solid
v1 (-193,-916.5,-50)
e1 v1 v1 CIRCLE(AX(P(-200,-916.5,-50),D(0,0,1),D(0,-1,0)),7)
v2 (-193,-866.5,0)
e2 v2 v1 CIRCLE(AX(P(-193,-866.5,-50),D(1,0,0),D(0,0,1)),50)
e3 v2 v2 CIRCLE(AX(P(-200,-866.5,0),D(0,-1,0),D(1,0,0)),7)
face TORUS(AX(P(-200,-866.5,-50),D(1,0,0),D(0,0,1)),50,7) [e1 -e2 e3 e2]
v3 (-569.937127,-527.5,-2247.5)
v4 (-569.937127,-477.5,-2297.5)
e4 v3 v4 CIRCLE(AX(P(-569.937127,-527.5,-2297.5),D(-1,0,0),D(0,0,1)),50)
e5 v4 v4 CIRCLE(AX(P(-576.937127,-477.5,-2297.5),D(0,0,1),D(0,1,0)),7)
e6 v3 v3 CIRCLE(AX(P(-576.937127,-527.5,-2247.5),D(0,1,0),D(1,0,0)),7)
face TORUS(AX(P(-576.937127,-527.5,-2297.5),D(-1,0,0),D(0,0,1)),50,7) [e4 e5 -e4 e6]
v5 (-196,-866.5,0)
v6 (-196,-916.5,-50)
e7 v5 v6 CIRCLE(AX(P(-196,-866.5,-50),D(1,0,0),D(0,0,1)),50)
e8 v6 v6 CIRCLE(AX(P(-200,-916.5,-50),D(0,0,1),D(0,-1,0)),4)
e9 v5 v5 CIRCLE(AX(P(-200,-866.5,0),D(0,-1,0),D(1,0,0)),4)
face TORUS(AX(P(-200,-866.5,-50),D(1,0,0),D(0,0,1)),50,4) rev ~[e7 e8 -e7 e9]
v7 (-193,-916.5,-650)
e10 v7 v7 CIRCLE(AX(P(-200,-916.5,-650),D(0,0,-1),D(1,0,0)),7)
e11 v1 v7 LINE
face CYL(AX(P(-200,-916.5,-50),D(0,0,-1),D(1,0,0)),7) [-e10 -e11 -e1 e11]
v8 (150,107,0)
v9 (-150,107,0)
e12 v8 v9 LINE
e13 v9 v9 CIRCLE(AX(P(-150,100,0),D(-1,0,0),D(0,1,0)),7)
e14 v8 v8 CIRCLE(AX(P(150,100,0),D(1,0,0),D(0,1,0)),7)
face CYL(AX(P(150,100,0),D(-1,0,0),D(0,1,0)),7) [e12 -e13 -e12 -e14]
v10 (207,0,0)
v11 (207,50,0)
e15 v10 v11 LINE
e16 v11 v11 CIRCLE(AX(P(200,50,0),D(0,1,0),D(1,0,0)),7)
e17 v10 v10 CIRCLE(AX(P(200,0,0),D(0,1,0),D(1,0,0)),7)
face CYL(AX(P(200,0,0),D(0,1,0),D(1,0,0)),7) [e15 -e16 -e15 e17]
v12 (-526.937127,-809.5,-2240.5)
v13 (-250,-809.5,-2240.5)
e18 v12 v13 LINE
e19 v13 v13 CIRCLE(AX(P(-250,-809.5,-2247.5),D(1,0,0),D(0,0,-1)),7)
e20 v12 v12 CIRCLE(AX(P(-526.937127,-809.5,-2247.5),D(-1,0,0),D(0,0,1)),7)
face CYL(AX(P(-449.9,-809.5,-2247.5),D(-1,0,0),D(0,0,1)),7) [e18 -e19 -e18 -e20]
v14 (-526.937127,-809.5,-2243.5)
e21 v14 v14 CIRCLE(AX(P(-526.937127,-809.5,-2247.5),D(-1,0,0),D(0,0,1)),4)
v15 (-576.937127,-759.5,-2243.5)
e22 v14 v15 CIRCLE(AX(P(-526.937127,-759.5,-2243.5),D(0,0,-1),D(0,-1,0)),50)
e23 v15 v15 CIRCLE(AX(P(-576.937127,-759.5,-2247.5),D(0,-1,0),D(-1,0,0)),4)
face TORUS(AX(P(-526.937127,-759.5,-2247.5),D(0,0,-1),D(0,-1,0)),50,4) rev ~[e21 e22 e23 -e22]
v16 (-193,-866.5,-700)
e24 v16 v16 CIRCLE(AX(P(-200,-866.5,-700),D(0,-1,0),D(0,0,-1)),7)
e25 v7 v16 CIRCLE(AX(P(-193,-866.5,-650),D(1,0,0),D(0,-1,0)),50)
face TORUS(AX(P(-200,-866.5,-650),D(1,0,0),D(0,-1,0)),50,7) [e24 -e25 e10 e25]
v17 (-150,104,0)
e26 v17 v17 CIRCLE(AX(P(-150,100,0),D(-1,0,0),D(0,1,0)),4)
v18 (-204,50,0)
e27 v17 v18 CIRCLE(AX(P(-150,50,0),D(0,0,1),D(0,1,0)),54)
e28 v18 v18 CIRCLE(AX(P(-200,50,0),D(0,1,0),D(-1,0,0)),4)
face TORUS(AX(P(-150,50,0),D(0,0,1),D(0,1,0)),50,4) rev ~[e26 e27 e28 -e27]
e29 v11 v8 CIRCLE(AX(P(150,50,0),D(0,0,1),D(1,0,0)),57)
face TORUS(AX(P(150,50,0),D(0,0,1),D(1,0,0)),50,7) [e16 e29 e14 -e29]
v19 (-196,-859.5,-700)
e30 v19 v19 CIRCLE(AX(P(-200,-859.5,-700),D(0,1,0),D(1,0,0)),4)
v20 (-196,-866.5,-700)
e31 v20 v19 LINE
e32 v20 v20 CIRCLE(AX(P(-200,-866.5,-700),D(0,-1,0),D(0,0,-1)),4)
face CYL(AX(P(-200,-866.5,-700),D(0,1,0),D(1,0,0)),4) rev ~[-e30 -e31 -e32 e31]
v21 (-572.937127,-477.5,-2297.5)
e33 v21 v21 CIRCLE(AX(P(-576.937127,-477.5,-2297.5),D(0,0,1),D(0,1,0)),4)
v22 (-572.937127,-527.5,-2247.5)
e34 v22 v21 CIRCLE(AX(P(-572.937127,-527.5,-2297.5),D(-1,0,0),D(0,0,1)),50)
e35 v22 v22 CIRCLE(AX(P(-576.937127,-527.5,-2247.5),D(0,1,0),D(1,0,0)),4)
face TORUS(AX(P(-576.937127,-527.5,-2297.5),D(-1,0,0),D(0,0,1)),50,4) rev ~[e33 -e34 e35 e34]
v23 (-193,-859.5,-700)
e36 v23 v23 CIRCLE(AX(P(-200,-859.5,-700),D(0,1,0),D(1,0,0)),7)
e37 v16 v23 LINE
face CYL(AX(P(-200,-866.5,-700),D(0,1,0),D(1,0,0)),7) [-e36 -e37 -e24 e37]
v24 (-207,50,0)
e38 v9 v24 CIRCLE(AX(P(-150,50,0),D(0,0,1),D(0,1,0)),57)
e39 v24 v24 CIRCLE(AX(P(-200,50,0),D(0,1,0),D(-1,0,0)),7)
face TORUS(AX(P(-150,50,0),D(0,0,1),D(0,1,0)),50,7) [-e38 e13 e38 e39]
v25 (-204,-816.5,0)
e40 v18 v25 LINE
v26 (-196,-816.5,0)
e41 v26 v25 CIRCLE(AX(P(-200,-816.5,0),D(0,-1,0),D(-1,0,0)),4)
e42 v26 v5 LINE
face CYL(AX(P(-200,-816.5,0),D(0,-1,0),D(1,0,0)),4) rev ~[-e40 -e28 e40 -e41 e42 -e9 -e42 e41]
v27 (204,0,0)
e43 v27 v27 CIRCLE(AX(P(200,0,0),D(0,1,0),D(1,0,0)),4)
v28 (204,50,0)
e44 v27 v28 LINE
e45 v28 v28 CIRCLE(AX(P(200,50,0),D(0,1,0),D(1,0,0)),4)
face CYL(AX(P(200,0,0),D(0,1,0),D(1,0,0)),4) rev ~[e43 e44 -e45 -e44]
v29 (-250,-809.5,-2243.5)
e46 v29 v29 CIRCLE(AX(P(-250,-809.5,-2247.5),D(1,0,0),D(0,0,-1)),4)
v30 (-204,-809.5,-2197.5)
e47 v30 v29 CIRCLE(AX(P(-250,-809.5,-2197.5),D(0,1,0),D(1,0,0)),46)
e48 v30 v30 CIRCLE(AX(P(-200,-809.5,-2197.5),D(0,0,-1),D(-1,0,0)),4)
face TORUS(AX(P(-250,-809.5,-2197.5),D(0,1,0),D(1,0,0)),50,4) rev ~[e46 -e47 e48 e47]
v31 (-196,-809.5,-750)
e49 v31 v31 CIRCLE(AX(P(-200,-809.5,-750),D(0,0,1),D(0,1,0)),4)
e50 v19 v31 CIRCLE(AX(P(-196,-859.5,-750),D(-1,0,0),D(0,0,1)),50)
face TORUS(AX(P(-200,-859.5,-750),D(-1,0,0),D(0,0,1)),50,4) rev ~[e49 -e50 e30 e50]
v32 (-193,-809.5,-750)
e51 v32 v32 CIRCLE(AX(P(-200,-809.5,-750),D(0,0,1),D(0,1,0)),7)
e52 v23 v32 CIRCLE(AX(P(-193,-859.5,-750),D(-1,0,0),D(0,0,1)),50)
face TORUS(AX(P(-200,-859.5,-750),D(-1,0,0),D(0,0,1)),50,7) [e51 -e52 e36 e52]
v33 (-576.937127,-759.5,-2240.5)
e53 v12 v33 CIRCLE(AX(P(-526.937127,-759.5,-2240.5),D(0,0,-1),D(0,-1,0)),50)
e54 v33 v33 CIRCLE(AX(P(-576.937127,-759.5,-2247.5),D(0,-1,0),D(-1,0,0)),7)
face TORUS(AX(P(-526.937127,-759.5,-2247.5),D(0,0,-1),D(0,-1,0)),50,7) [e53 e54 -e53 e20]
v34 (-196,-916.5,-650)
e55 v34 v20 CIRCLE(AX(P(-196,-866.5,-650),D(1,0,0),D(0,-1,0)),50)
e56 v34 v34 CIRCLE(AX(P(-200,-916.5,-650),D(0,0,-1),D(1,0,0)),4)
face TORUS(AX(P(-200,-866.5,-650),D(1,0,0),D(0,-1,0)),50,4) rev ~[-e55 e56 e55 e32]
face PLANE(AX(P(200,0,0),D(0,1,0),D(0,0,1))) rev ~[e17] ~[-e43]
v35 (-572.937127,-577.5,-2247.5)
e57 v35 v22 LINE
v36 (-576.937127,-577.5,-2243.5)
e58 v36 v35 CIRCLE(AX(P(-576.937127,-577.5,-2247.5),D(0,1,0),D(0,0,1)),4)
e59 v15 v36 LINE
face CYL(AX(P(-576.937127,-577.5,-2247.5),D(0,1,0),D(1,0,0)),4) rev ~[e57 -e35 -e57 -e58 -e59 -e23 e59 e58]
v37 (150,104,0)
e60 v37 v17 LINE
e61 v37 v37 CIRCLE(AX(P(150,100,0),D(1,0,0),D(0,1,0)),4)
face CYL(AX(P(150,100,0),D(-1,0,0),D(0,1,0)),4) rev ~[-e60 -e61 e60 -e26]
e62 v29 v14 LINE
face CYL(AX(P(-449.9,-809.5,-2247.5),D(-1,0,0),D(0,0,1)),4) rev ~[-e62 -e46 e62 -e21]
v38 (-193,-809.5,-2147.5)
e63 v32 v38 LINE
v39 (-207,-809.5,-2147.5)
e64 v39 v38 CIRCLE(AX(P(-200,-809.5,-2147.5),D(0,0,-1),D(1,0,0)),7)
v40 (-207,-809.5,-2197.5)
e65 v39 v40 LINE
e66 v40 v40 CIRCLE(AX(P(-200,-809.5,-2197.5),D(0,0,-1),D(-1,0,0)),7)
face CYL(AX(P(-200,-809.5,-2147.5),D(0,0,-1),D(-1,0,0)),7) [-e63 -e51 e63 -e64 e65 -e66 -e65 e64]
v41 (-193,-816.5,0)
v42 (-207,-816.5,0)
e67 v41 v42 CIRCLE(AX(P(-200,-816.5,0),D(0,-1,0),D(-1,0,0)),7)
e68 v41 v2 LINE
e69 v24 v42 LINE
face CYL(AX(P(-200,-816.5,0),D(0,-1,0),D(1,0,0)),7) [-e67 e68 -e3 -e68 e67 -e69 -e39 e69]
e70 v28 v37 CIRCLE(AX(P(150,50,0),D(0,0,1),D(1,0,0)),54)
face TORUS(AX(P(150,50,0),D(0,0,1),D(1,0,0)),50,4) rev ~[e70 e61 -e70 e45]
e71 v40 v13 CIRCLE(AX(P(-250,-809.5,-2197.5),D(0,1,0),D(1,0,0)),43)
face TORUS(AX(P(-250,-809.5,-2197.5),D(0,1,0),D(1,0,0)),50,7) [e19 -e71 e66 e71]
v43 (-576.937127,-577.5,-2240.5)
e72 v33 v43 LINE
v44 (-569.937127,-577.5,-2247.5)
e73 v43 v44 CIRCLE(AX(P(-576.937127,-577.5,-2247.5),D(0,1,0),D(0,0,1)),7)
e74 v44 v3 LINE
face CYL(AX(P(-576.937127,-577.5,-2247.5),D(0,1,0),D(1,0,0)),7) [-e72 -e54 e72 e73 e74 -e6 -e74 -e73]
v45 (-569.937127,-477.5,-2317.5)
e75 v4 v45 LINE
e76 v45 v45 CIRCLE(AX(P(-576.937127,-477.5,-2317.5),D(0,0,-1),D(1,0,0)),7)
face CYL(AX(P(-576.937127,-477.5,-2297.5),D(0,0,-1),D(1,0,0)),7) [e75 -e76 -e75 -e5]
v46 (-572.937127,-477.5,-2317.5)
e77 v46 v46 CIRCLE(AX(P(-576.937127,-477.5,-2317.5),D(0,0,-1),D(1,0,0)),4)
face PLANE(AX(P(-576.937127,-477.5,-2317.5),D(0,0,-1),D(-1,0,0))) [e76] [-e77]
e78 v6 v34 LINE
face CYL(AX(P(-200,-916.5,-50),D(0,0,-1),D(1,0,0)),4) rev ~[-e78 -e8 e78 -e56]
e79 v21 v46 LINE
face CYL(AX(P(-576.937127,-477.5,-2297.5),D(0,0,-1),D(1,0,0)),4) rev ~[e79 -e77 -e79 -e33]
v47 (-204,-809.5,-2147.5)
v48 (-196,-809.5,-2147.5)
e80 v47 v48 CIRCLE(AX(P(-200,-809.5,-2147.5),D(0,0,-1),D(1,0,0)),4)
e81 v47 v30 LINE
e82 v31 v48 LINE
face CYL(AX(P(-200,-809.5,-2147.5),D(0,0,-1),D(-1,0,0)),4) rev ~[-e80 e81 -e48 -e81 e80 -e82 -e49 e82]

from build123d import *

# Parameters (mm, degrees)
SKETCH_2_R    = 7
SKETCH_2_R_2  = 4
SKETCH_4_R    = 7
SKETCH_4_R_2  = 4
SKETCH_6_R    = 7
SKETCH_6_R_2  = 4
SKETCH_8_R    = 7
SKETCH_8_R_2  = 4
SKETCH_10_R   = 7
SKETCH_10_R_2 = 4


with BuildPart() as part:
    # Sweep 1: sweep along a path in Sketch 1
    with BuildLine(Plane.XY) as sweep_1_path:
        Line((200, 0), (200, 50))
        ThreePointArc((200, 50), (185.355339059, 85.355339059), (150, 100))
        Line((150, 100), (-150, 100))
        ThreePointArc((-150, 100), (-185.355339059, 85.355339059), (-200, 50))
        Line((-200, 50), (-200, -816.5))
    # Sketch 2 → Sweep 1 (sweep)
    with BuildSketch(Plane(origin=(0, 0, 0), x_dir=(1, 0, 0), z_dir=(0, 1, 0))):
        with Locations((200, 0)):
            Circle(SKETCH_2_R)
        with Locations((200, 0)):
            Circle(SKETCH_2_R_2, mode=Mode.SUBTRACT)
    sweep(path=sweep_1_path.line)

    # Sweep 2: sweep along a path in Sketch 3
    with BuildLine(Plane(origin=(-200, 0, 0), x_dir=(0, 0, -1), z_dir=(1, 0, 0))) as sweep_2_path:
        Line((0, -816.5), (0, -866.5))
        ThreePointArc((0, -866.5), (14.644660941, -901.855339059), (50, -916.5))
        Line((50, -916.5), (650, -916.5))
        ThreePointArc((650, -916.5), (685.355339059, -901.855339059), (700, -866.5))
        Line((700, -866.5), (700, -859.5))
        ThreePointArc((700, -859.5), (714.644660941, -824.144660941), (750, -809.5))
        Line((750, -809.5), (2147.5, -809.5))
    # Sketch 4 → Sweep 2 (sweep)
    with BuildSketch(Plane.XZ.offset(816.5)):
        with Locations((-200, 0)):
            Circle(SKETCH_4_R)
        with Locations((-200, 0)):
            Circle(SKETCH_4_R_2, mode=Mode.SUBTRACT)
    sweep(path=sweep_2_path.line)

    # Sweep 3: sweep along a path in Sketch 5
    with BuildLine(Plane(origin=(0, -809.5, 0), x_dir=(1, 0, 0), z_dir=(0, 1, 0))) as sweep_3_path:
        Line((-200, 2147.5), (-200, 2197.5))
        ThreePointArc((-200, 2197.5), (-214.644660941, 2232.855339059), (-250, 2247.5))
        Line((-250, 2247.5), (-449.9, 2247.5))
    # Sketch 6 → Sweep 3 (sweep)
    with BuildSketch(Plane(origin=(0, 0, -2147.5), x_dir=(-1, 0, 0), z_dir=(0, 0, -1))):
        with Locations((200, -809.5)):
            Circle(SKETCH_6_R)
        with Locations((200, -809.5)):
            Circle(SKETCH_6_R_2, mode=Mode.SUBTRACT)
    sweep(path=sweep_3_path.line)

    # Sweep 4: sweep along a path in Sketch 7
    with BuildLine(Plane.XY.offset(-2247.5)) as sweep_4_path:
        Line((-449.9, -809.5), (-526.937126848, -809.5))
        ThreePointArc((-526.937126848, -809.5), (-562.292465907, -794.855339059), (-576.937126848, -759.5))
        Line((-576.937126848, -759.5), (-576.937126848, -577.5))
    # Sketch 8 → Sweep 4 (sweep)
    with BuildSketch(Plane.ZY.offset(449.9)):
        with Locations((-2247.5, -809.5)):
            Circle(SKETCH_8_R)
        with Locations((-2247.5, -809.5)):
            Circle(SKETCH_8_R_2, mode=Mode.SUBTRACT)
    sweep(path=sweep_4_path.line)

    # Sweep 5: sweep along a path in Sketch 9
    with BuildLine(Plane(origin=(-576.937126848, 0, 0), x_dir=(0, 0, -1), z_dir=(1, 0, 0))) as sweep_5_path:
        Line((2247.5, -577.5), (2247.5, -527.5))
        ThreePointArc((2247.5, -527.5), (2262.144660941, -492.144660941), (2297.5, -477.5))
        Line((2297.5, -477.5), (2317.5, -477.5))
    # Sketch 10 → Sweep 5 (sweep)
    with BuildSketch(Plane(origin=(0, -577.5, 0), x_dir=(1, 0, 0), z_dir=(0, 1, 0))):
        with Locations((-576.937126848, 2247.5)):
            Circle(SKETCH_10_R)
        with Locations((-576.937126848, 2247.5)):
            Circle(SKETCH_10_R_2, mode=Mode.SUBTRACT)
    sweep(path=sweep_5_path.line)


solid = part.part
